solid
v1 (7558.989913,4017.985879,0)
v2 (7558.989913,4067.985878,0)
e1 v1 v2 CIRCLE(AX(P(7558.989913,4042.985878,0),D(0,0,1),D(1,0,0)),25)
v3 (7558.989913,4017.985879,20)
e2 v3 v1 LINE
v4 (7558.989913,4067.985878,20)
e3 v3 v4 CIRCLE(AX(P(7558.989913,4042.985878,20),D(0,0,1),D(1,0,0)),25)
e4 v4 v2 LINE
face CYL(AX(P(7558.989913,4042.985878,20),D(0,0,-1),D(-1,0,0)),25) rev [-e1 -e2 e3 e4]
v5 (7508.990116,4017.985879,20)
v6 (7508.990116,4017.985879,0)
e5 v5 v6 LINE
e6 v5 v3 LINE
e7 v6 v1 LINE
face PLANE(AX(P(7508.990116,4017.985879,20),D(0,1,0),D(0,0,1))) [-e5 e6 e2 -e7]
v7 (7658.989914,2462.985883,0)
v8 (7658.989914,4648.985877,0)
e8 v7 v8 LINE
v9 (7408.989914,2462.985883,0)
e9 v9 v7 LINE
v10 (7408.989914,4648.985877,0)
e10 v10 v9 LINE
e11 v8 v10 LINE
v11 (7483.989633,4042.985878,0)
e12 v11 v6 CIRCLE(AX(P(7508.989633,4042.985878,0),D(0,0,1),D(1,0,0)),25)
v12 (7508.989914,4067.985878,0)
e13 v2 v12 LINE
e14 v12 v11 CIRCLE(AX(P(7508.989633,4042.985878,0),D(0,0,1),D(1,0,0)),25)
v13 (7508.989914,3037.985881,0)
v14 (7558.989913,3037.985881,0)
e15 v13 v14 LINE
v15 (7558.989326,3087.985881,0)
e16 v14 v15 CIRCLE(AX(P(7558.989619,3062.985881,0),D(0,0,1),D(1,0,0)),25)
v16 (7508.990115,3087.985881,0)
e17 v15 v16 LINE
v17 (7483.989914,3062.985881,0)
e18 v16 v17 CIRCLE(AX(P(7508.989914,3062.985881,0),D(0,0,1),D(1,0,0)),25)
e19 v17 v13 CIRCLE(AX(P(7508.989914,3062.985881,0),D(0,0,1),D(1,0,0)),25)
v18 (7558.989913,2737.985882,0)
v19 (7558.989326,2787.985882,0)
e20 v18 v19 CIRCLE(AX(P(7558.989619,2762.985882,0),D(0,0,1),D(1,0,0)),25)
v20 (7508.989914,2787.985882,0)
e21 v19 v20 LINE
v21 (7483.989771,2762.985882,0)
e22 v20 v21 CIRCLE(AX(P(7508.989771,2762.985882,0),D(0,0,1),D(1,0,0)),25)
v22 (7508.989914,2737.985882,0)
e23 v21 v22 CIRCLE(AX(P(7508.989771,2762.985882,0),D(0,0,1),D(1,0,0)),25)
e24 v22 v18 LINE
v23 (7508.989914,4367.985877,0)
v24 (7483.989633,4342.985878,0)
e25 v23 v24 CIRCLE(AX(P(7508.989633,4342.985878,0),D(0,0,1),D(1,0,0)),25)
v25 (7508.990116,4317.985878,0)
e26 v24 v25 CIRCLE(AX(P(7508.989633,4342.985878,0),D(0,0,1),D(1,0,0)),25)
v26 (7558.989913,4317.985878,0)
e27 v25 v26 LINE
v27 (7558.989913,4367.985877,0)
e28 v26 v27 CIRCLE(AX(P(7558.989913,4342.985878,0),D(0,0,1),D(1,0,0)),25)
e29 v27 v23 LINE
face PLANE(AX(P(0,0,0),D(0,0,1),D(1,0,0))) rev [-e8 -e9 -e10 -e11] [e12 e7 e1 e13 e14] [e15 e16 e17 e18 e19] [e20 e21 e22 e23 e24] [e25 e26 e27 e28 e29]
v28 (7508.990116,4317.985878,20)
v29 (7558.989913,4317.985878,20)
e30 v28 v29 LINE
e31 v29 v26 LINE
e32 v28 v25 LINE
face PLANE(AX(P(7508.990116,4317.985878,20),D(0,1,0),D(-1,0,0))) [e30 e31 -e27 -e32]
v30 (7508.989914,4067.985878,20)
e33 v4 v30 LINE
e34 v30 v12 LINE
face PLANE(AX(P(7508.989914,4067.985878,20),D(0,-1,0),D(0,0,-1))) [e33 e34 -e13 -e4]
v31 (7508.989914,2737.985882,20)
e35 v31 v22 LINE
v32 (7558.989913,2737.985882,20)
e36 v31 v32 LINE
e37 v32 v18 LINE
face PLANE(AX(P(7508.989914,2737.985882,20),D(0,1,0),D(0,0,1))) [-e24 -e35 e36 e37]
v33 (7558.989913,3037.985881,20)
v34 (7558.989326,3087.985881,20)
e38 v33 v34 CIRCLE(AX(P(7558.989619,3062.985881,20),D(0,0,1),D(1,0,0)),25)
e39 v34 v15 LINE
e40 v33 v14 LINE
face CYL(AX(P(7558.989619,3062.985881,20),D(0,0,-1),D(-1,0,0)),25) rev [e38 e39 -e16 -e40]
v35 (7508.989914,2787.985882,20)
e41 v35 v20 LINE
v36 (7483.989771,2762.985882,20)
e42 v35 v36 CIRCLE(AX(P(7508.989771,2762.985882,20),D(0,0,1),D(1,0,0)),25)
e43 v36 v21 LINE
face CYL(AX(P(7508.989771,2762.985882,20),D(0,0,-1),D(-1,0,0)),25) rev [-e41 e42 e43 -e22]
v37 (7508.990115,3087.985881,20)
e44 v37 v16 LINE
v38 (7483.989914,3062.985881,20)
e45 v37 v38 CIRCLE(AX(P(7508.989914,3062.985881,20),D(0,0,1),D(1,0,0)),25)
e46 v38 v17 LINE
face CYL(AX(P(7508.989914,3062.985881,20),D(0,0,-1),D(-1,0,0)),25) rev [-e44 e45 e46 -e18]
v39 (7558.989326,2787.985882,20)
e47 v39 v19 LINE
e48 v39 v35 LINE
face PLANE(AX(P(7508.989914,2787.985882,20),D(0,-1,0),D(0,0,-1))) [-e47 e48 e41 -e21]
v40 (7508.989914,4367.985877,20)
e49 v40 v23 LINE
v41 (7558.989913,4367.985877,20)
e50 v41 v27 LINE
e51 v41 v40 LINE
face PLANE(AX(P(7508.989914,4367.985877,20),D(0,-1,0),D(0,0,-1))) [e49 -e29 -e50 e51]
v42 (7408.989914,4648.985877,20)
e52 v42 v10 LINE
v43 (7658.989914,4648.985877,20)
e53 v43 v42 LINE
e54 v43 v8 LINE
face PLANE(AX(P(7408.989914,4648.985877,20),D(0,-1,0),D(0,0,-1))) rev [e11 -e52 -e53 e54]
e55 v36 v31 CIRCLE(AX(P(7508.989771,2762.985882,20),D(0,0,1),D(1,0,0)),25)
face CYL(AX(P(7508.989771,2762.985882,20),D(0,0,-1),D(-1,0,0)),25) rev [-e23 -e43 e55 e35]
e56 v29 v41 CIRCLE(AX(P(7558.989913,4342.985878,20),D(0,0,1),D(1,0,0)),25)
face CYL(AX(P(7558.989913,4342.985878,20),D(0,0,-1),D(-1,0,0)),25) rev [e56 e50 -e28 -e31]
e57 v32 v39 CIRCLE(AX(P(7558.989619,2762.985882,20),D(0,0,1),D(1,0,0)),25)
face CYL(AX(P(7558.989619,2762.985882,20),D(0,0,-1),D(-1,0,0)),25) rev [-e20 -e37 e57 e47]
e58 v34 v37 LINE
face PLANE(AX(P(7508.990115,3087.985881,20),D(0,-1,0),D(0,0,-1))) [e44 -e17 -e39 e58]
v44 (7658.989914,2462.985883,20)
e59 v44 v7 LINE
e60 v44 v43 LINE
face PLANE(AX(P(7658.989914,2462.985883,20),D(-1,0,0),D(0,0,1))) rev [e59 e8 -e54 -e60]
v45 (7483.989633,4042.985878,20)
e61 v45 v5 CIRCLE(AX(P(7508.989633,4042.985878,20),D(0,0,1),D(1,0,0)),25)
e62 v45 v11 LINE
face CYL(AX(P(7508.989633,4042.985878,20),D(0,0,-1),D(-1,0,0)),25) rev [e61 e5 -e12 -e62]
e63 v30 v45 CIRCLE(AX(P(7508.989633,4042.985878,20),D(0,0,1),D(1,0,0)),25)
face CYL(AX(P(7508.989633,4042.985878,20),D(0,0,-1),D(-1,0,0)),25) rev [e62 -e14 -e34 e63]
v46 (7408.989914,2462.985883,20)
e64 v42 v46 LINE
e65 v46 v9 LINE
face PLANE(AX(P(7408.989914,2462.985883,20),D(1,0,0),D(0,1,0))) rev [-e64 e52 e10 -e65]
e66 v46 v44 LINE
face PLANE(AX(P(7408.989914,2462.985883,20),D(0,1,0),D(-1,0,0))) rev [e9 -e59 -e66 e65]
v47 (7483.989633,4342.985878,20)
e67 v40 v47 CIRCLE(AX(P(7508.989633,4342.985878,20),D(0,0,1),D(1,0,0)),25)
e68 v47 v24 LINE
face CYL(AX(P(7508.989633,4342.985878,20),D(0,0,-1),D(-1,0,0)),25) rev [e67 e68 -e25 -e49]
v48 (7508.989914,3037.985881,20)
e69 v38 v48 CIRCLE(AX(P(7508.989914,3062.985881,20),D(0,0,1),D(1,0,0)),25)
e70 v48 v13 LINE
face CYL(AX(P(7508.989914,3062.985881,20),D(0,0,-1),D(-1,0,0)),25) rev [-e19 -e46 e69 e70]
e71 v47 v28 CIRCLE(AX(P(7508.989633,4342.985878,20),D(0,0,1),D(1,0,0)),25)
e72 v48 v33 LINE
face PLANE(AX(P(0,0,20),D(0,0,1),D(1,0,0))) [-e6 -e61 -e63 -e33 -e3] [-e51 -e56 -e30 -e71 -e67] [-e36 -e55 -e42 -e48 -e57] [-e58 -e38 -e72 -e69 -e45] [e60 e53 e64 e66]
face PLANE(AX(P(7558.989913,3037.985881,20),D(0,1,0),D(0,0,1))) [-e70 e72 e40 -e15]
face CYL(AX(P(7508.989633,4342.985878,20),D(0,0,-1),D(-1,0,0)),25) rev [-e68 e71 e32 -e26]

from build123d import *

# Parameters (mm, degrees)
BOSS_EXTRUDE1_DEPTH = 20


with BuildPart() as part:
    # Sketch1 → Boss-Extrude1 (new body)
    with BuildSketch(Plane.XY):
        Polygon((7408.989913804, 2462.985883167), (7408.989913804, 4648.985876948), (7658.989913804, 4648.985876948), (7658.989913804, 2462.985883253), align=None)
        with BuildLine():
            Line((7508.989913506, 4367.985877479), (7558.989913353, 4367.985877479))
            ThreePointArc((7558.989913353, 4367.985877479), (7583.98991328, 4342.985877555), (7558.989913357, 4317.985877628))
            Line((7558.989913357, 4317.985877628), (7508.99011555, 4317.985877628))
            ThreePointArc((7508.99011555, 4317.985877628), (7483.989632688, 4342.98577653), (7508.989913506, 4367.985877479))
        make_face(mode=Mode.SUBTRACT)
        with BuildLine():
            Line((7508.990115362, 3087.985881301), (7558.98932559, 3087.985881301))
            ThreePointArc((7558.98932559, 3087.985881301), (7583.989619399, 3062.986175259), (7558.989913357, 3037.98588145))
            Line((7558.989913357, 3037.98588145), (7508.989913506, 3037.98588145))
            ThreePointArc((7508.989913506, 3037.98588145), (7483.989913645, 3062.985982304), (7508.990115362, 3087.985881301))
        make_face(mode=Mode.SUBTRACT)
        with BuildLine():
            Line((7508.989913506, 4067.985878375), (7558.989913353, 4067.985878375))
            ThreePointArc((7558.989913353, 4067.985878375), (7583.989913278, 4042.985878449), (7558.989913353, 4017.985878524))
            Line((7558.989913353, 4017.985878524), (7508.990115553, 4017.985878524))
            ThreePointArc((7508.990115553, 4017.985878524), (7483.989632674, 4042.985777424), (7508.989913506, 4067.985878375))
        make_face(mode=Mode.SUBTRACT)
        with BuildLine():
            Line((7508.989913506, 2787.985882197), (7558.989325591, 2787.985882197))
            ThreePointArc((7558.989325591, 2787.985882197), (7583.989619399, 2762.986176154), (7558.989913357, 2737.985882346))
            Line((7558.989913357, 2737.985882346), (7508.989913506, 2737.985882346))
            ThreePointArc((7508.989913506, 2737.985882346), (7483.989770854, 2762.985882271), (7508.989913506, 2787.985882197))
        make_face(mode=Mode.SUBTRACT)
    extrude(amount=BOSS_EXTRUDE1_DEPTH)


solid = part.part
